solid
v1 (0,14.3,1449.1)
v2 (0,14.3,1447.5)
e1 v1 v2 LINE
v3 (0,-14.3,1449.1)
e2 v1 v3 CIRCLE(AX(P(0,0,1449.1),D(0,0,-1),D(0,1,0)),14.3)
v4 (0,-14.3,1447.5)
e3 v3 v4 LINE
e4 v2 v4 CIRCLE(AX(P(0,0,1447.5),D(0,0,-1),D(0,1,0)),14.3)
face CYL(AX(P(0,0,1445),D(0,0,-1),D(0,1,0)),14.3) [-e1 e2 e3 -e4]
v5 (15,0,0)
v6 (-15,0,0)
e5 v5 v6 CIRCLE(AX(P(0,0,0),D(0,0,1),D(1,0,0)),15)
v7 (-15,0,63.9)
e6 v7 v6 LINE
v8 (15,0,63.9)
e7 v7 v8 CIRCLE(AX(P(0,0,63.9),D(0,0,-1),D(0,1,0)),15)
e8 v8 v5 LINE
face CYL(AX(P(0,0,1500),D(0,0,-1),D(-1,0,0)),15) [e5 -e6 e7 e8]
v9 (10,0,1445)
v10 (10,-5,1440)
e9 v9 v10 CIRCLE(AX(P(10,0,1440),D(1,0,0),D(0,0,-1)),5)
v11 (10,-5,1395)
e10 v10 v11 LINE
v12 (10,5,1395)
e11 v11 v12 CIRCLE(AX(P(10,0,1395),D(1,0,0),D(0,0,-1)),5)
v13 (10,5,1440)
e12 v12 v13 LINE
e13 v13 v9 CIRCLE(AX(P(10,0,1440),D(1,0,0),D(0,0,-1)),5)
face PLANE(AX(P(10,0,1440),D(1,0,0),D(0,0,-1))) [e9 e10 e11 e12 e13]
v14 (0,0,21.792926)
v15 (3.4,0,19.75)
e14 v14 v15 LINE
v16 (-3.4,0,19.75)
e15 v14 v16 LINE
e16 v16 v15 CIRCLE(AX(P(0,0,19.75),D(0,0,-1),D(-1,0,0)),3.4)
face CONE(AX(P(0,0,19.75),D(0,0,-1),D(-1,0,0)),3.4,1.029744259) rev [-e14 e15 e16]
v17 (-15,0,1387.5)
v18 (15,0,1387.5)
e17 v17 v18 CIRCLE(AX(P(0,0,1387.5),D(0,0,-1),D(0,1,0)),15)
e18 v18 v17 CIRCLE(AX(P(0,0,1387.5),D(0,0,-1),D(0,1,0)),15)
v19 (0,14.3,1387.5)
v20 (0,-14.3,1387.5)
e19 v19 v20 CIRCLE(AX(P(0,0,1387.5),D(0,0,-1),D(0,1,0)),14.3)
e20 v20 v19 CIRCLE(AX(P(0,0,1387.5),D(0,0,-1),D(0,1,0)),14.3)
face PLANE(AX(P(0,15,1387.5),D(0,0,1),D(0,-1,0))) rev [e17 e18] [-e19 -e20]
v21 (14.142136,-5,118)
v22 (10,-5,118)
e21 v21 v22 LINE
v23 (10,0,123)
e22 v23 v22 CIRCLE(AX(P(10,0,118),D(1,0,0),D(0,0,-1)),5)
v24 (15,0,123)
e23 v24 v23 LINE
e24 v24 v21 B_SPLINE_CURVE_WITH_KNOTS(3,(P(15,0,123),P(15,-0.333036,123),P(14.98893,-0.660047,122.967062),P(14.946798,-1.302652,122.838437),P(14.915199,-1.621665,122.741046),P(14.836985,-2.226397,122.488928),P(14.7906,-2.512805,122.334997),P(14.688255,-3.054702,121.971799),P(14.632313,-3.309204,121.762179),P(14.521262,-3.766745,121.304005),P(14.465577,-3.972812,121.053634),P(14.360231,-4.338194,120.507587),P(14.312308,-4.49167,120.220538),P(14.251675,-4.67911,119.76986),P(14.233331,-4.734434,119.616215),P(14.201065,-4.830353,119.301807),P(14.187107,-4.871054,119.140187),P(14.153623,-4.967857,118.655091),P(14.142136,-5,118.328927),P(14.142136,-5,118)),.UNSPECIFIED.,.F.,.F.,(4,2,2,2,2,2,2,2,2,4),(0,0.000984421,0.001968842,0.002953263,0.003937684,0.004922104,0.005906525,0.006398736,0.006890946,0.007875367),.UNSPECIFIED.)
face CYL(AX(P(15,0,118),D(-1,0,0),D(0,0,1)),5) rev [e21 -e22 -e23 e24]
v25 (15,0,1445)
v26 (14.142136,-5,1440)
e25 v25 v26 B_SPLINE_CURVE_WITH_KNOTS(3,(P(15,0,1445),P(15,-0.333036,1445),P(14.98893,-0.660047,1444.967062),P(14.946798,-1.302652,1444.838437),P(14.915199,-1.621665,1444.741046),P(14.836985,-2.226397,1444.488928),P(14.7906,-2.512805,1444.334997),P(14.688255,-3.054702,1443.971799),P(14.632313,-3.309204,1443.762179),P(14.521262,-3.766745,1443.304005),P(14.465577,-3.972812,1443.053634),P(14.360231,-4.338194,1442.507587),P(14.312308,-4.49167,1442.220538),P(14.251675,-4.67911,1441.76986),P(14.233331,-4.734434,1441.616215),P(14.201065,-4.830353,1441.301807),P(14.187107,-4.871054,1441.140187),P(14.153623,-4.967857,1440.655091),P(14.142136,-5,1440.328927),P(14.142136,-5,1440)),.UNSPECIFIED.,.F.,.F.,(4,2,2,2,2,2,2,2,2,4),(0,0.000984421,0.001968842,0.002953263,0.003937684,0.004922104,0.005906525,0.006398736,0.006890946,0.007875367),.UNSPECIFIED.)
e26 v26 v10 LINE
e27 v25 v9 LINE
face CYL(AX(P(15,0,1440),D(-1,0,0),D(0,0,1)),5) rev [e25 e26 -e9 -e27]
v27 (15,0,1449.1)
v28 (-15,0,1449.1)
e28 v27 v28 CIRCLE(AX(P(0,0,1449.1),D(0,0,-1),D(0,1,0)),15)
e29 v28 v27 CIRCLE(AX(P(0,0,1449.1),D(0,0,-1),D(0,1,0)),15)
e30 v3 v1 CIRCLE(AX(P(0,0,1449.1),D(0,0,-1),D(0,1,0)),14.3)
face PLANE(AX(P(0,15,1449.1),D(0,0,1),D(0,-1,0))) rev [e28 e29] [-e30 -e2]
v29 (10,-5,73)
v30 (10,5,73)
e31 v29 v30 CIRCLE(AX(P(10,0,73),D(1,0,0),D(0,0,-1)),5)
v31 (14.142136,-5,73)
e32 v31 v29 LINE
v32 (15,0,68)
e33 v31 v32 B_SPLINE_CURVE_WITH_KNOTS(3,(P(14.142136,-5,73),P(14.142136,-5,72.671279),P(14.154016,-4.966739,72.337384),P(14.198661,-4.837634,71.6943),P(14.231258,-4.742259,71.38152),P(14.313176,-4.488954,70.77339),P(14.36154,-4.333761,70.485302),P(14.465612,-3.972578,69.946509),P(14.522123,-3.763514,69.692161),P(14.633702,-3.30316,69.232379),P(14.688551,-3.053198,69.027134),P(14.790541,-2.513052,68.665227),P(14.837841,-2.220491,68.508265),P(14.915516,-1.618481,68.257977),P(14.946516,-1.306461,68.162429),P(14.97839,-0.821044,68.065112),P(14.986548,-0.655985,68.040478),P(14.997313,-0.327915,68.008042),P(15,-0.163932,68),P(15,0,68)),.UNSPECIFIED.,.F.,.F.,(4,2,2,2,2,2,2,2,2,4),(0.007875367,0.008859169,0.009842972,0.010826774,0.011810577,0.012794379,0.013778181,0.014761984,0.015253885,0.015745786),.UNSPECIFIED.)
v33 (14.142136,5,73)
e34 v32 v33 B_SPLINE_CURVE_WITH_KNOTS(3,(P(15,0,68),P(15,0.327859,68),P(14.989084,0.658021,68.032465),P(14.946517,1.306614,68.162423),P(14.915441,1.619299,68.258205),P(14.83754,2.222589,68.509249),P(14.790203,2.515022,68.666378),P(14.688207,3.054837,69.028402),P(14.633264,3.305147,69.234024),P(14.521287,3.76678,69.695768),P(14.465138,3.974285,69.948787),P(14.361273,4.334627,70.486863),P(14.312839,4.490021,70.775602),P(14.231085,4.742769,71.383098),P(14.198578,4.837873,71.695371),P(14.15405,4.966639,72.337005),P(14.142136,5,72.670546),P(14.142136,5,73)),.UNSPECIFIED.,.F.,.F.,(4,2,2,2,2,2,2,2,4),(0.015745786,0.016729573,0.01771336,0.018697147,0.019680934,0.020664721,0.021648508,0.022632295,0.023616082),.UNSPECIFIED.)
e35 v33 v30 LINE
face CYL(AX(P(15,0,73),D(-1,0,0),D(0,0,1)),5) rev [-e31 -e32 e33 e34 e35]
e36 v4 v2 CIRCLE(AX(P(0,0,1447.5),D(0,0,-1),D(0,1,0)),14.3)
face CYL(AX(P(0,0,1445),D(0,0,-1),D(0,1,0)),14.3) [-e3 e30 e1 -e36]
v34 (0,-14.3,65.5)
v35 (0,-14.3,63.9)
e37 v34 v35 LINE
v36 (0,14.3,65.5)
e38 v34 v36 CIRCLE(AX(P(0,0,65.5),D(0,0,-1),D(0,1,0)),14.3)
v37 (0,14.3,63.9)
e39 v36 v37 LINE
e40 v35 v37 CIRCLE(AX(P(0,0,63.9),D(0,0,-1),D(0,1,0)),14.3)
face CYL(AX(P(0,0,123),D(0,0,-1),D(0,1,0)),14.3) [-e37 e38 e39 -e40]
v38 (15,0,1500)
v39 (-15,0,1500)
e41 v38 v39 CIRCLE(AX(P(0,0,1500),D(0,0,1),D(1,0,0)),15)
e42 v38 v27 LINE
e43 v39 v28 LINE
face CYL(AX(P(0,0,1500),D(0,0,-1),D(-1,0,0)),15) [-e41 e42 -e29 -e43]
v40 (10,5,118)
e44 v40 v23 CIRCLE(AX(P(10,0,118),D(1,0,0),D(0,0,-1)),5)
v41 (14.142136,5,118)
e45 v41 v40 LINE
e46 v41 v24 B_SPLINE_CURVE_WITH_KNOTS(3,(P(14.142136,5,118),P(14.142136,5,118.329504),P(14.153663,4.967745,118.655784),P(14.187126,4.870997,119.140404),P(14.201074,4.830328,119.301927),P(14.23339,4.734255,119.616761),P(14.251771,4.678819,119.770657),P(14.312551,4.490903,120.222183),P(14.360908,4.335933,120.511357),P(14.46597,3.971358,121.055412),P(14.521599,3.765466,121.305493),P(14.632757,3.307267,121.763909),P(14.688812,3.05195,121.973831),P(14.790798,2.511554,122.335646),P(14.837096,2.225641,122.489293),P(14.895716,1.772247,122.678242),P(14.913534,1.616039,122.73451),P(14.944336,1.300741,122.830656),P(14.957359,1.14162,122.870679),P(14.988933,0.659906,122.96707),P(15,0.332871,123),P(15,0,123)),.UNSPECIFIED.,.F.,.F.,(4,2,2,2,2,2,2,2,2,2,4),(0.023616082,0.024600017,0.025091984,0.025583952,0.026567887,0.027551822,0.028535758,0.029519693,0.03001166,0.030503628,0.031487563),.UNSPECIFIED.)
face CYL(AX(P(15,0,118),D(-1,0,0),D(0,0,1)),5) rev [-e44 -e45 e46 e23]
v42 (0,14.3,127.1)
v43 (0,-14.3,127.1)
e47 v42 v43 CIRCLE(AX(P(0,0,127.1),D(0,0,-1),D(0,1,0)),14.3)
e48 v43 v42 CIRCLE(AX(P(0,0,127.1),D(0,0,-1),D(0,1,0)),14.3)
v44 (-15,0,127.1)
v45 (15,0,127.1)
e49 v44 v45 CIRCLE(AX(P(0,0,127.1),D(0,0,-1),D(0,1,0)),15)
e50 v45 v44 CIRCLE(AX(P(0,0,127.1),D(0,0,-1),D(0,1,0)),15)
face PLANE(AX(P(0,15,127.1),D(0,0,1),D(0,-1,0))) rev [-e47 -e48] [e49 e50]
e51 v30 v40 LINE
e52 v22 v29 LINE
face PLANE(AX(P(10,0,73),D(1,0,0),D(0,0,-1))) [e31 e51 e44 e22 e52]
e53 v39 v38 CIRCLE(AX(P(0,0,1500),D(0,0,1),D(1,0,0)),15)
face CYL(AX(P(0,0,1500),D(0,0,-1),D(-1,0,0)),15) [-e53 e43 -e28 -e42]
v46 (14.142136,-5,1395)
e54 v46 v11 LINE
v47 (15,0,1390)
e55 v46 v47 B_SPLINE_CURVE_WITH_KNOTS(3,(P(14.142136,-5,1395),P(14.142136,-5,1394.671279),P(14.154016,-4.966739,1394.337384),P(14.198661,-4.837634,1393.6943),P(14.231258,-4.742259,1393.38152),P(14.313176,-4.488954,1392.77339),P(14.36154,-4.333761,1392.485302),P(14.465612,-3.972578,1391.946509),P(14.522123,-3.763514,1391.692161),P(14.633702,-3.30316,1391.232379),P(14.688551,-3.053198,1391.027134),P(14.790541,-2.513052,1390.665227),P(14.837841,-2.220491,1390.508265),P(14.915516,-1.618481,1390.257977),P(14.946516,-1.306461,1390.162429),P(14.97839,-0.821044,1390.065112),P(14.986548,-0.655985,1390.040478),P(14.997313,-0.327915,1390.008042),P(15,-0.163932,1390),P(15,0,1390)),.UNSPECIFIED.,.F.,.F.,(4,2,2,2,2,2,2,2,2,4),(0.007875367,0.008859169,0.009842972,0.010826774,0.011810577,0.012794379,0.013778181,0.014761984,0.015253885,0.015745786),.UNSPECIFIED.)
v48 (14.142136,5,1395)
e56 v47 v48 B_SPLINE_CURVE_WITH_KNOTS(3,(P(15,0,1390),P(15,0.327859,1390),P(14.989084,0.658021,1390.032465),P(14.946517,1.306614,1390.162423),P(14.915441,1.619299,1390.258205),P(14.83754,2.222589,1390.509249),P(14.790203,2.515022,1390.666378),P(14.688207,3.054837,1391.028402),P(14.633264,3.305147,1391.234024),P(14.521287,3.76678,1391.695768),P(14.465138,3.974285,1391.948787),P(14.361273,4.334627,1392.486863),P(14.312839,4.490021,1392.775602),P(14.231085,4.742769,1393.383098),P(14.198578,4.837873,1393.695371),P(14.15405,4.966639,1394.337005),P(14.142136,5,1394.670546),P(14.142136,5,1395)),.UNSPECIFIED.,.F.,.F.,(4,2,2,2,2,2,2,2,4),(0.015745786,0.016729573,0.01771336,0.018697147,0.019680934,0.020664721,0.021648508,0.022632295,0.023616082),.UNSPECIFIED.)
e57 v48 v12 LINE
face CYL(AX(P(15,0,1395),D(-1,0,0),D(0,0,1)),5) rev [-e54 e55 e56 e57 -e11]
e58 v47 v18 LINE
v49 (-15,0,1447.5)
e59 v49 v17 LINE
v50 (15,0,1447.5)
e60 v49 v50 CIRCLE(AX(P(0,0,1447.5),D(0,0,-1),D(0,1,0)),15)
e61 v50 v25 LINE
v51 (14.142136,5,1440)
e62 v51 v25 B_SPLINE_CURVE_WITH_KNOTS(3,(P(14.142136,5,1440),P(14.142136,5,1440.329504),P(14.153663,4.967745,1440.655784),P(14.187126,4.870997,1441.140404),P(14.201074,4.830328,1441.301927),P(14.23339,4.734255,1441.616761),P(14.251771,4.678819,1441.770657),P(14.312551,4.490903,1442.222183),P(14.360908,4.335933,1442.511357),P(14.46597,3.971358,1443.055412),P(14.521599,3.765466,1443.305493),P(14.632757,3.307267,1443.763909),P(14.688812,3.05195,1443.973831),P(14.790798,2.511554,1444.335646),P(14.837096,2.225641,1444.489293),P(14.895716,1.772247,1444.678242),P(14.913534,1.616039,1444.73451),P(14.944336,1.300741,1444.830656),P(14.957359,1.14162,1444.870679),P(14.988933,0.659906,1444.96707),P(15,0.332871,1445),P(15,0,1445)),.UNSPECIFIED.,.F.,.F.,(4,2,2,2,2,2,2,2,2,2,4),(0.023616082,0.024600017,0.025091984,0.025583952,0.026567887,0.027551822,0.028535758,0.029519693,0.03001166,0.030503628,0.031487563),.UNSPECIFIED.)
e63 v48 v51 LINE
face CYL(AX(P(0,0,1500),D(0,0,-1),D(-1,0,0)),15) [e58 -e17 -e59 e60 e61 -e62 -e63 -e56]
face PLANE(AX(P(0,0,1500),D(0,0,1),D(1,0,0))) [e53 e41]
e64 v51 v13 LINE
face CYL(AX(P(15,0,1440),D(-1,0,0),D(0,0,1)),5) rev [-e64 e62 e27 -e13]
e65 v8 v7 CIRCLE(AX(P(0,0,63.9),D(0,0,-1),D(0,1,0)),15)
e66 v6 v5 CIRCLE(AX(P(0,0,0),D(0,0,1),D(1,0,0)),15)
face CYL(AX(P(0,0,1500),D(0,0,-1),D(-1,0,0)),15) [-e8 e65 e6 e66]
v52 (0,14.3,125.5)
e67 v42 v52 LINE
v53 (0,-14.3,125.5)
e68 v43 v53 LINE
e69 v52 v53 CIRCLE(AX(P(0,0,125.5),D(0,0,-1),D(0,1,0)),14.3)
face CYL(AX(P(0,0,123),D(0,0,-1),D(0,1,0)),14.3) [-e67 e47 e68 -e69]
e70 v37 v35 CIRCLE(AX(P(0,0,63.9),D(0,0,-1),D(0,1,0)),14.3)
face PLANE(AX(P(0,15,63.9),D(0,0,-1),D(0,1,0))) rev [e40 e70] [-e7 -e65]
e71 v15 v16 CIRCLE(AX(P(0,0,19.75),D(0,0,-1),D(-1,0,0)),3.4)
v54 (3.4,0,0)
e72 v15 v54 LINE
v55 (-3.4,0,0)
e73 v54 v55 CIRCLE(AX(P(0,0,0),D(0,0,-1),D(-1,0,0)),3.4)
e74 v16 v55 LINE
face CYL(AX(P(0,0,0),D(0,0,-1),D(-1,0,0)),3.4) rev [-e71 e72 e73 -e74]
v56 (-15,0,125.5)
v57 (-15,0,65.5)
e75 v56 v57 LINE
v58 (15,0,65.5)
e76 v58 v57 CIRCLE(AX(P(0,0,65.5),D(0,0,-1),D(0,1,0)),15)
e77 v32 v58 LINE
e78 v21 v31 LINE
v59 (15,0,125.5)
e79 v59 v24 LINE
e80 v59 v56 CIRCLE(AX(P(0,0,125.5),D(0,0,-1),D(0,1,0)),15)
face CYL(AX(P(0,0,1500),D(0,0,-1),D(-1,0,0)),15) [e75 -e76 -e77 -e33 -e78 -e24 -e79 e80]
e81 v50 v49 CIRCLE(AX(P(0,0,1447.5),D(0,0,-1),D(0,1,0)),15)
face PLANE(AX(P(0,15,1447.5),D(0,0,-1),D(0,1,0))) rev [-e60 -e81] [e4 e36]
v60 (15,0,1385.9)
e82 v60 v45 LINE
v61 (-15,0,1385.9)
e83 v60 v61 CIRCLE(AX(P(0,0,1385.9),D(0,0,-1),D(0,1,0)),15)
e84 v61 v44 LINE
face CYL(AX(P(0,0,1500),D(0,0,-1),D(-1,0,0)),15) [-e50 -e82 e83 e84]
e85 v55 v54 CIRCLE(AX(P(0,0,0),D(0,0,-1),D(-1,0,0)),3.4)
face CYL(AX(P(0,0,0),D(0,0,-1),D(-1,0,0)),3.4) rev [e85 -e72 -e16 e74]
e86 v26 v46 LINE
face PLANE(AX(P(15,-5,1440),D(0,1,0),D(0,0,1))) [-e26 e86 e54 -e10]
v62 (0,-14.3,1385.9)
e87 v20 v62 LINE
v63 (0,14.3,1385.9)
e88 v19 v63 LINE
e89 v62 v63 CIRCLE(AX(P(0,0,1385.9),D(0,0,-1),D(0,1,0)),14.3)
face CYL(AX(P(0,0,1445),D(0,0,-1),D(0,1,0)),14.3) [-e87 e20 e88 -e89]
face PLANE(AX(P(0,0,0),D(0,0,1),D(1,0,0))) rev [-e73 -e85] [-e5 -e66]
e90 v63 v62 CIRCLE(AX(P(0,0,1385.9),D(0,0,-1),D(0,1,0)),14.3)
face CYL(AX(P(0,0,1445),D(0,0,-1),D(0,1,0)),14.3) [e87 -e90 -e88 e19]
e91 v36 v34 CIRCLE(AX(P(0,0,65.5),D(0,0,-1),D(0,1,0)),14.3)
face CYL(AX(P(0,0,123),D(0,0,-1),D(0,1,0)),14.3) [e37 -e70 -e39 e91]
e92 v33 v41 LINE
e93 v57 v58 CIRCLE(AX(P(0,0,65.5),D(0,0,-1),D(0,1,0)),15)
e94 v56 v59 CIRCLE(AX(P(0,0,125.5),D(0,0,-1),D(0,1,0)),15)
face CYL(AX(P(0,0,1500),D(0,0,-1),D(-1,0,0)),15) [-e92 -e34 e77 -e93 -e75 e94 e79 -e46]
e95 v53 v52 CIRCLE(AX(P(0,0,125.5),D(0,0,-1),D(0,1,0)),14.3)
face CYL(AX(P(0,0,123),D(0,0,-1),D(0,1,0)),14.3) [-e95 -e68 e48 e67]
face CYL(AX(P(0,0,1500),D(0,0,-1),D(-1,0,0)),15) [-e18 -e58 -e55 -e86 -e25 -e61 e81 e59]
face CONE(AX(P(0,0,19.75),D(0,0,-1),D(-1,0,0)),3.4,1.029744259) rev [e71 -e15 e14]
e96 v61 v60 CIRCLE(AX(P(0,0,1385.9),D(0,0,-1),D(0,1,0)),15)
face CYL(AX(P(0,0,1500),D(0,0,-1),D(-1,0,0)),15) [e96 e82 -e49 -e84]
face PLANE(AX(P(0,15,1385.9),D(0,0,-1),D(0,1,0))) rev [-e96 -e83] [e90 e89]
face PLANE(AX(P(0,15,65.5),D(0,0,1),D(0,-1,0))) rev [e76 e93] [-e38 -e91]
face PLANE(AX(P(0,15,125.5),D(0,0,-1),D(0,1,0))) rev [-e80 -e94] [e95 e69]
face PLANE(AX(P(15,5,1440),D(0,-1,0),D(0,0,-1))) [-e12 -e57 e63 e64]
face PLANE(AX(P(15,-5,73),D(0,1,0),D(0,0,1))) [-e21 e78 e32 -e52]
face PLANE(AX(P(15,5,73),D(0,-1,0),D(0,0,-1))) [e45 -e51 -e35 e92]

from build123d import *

# Parameters (mm, degrees)
SKETCH_2_R             = 15
EXTRUDE_1_DEPTH        = 1500
CUT_EXTRUDE_1_DEPTH    = 1501.283306579
SKETCH_4_W             = 1.6
SKETCH_4_H             = 0.7
PATTERN_LINEAR_1_COUNT = 2
PATTERN_LINEAR_1_PITCH = 1322
HOLE_WIZARD_M8_1_D     = 6.8
HOLE_WIZARD_M8_1_DEPTH = 19.75
HOLE_WIZARD_M8_1_TIP   = 2.042926105


with BuildPart() as part:
    # 草图2 → 凸台-拉伸1 (new body)
    with BuildSketch(Plane.XY):
        Circle(SKETCH_2_R)
    extrude(amount=EXTRUDE_1_DEPTH)

    # 草图3 → 切除-拉伸1 (cut, through all)
    with BuildSketch(Plane(origin=(10, 0, 0), x_dir=(0, 0, -1), z_dir=(1, 0, 0))):
        with BuildLine():
            Line((-1440, 5), (-1395, 5))
            ThreePointArc((-1395, 5), (-1390, 0), (-1395, -5))
            Line((-1395, -5), (-1440, -5))
            ThreePointArc((-1440, -5), (-1445, 0), (-1440, 5))
        make_face()
        with BuildLine():
            Line((-73, -5), (-118, -5))
            ThreePointArc((-118, -5), (-123, 0), (-118, 5))
            Line((-118, 5), (-73, 5))
            ThreePointArc((-73, 5), (-68, 0), (-73, -5))
        make_face()
    extrude(amount=CUT_EXTRUDE_1_DEPTH, mode=Mode.SUBTRACT)

    # 草图4 → 切除-旋转5 (revolve, cut)
    with BuildSketch(Plane(origin=(0, 0, 0), x_dir=(0, 0, -1), z_dir=(1, 0, 0))):
        with Locations((-1448.3, 14.65)):
            Rectangle(SKETCH_4_W, SKETCH_4_H)
        with Locations((-1386.7, 14.65)):
            Rectangle(SKETCH_4_W, SKETCH_4_H)
    cut_revolve_5 = revolve(axis=Axis((0, 0, 1445), (0, 0, 1)), mode=Mode.SUBTRACT)

    # 阵列(线性)1: 切除-旋转5 ×2
    with Locations(*[(0, 0, -i * PATTERN_LINEAR_1_PITCH) for i in range(1, PATTERN_LINEAR_1_COUNT)]):
        add(cut_revolve_5, mode=Mode.SUBTRACT)

    # M8 螺纹孔1
    with Locations(Plane(origin=(0, 0, 0), x_dir=(-1, 0, 0), z_dir=(0, 0, -1))):
        with Locations((0, 0)):
            Hole(HOLE_WIZARD_M8_1_D / 2, depth=HOLE_WIZARD_M8_1_DEPTH)
            with Locations((0, 0, -(HOLE_WIZARD_M8_1_DEPTH + HOLE_WIZARD_M8_1_TIP / 2))):  # 118° drill point
                Cone(0, HOLE_WIZARD_M8_1_D / 2, HOLE_WIZARD_M8_1_TIP, mode=Mode.SUBTRACT)


solid = part.part
